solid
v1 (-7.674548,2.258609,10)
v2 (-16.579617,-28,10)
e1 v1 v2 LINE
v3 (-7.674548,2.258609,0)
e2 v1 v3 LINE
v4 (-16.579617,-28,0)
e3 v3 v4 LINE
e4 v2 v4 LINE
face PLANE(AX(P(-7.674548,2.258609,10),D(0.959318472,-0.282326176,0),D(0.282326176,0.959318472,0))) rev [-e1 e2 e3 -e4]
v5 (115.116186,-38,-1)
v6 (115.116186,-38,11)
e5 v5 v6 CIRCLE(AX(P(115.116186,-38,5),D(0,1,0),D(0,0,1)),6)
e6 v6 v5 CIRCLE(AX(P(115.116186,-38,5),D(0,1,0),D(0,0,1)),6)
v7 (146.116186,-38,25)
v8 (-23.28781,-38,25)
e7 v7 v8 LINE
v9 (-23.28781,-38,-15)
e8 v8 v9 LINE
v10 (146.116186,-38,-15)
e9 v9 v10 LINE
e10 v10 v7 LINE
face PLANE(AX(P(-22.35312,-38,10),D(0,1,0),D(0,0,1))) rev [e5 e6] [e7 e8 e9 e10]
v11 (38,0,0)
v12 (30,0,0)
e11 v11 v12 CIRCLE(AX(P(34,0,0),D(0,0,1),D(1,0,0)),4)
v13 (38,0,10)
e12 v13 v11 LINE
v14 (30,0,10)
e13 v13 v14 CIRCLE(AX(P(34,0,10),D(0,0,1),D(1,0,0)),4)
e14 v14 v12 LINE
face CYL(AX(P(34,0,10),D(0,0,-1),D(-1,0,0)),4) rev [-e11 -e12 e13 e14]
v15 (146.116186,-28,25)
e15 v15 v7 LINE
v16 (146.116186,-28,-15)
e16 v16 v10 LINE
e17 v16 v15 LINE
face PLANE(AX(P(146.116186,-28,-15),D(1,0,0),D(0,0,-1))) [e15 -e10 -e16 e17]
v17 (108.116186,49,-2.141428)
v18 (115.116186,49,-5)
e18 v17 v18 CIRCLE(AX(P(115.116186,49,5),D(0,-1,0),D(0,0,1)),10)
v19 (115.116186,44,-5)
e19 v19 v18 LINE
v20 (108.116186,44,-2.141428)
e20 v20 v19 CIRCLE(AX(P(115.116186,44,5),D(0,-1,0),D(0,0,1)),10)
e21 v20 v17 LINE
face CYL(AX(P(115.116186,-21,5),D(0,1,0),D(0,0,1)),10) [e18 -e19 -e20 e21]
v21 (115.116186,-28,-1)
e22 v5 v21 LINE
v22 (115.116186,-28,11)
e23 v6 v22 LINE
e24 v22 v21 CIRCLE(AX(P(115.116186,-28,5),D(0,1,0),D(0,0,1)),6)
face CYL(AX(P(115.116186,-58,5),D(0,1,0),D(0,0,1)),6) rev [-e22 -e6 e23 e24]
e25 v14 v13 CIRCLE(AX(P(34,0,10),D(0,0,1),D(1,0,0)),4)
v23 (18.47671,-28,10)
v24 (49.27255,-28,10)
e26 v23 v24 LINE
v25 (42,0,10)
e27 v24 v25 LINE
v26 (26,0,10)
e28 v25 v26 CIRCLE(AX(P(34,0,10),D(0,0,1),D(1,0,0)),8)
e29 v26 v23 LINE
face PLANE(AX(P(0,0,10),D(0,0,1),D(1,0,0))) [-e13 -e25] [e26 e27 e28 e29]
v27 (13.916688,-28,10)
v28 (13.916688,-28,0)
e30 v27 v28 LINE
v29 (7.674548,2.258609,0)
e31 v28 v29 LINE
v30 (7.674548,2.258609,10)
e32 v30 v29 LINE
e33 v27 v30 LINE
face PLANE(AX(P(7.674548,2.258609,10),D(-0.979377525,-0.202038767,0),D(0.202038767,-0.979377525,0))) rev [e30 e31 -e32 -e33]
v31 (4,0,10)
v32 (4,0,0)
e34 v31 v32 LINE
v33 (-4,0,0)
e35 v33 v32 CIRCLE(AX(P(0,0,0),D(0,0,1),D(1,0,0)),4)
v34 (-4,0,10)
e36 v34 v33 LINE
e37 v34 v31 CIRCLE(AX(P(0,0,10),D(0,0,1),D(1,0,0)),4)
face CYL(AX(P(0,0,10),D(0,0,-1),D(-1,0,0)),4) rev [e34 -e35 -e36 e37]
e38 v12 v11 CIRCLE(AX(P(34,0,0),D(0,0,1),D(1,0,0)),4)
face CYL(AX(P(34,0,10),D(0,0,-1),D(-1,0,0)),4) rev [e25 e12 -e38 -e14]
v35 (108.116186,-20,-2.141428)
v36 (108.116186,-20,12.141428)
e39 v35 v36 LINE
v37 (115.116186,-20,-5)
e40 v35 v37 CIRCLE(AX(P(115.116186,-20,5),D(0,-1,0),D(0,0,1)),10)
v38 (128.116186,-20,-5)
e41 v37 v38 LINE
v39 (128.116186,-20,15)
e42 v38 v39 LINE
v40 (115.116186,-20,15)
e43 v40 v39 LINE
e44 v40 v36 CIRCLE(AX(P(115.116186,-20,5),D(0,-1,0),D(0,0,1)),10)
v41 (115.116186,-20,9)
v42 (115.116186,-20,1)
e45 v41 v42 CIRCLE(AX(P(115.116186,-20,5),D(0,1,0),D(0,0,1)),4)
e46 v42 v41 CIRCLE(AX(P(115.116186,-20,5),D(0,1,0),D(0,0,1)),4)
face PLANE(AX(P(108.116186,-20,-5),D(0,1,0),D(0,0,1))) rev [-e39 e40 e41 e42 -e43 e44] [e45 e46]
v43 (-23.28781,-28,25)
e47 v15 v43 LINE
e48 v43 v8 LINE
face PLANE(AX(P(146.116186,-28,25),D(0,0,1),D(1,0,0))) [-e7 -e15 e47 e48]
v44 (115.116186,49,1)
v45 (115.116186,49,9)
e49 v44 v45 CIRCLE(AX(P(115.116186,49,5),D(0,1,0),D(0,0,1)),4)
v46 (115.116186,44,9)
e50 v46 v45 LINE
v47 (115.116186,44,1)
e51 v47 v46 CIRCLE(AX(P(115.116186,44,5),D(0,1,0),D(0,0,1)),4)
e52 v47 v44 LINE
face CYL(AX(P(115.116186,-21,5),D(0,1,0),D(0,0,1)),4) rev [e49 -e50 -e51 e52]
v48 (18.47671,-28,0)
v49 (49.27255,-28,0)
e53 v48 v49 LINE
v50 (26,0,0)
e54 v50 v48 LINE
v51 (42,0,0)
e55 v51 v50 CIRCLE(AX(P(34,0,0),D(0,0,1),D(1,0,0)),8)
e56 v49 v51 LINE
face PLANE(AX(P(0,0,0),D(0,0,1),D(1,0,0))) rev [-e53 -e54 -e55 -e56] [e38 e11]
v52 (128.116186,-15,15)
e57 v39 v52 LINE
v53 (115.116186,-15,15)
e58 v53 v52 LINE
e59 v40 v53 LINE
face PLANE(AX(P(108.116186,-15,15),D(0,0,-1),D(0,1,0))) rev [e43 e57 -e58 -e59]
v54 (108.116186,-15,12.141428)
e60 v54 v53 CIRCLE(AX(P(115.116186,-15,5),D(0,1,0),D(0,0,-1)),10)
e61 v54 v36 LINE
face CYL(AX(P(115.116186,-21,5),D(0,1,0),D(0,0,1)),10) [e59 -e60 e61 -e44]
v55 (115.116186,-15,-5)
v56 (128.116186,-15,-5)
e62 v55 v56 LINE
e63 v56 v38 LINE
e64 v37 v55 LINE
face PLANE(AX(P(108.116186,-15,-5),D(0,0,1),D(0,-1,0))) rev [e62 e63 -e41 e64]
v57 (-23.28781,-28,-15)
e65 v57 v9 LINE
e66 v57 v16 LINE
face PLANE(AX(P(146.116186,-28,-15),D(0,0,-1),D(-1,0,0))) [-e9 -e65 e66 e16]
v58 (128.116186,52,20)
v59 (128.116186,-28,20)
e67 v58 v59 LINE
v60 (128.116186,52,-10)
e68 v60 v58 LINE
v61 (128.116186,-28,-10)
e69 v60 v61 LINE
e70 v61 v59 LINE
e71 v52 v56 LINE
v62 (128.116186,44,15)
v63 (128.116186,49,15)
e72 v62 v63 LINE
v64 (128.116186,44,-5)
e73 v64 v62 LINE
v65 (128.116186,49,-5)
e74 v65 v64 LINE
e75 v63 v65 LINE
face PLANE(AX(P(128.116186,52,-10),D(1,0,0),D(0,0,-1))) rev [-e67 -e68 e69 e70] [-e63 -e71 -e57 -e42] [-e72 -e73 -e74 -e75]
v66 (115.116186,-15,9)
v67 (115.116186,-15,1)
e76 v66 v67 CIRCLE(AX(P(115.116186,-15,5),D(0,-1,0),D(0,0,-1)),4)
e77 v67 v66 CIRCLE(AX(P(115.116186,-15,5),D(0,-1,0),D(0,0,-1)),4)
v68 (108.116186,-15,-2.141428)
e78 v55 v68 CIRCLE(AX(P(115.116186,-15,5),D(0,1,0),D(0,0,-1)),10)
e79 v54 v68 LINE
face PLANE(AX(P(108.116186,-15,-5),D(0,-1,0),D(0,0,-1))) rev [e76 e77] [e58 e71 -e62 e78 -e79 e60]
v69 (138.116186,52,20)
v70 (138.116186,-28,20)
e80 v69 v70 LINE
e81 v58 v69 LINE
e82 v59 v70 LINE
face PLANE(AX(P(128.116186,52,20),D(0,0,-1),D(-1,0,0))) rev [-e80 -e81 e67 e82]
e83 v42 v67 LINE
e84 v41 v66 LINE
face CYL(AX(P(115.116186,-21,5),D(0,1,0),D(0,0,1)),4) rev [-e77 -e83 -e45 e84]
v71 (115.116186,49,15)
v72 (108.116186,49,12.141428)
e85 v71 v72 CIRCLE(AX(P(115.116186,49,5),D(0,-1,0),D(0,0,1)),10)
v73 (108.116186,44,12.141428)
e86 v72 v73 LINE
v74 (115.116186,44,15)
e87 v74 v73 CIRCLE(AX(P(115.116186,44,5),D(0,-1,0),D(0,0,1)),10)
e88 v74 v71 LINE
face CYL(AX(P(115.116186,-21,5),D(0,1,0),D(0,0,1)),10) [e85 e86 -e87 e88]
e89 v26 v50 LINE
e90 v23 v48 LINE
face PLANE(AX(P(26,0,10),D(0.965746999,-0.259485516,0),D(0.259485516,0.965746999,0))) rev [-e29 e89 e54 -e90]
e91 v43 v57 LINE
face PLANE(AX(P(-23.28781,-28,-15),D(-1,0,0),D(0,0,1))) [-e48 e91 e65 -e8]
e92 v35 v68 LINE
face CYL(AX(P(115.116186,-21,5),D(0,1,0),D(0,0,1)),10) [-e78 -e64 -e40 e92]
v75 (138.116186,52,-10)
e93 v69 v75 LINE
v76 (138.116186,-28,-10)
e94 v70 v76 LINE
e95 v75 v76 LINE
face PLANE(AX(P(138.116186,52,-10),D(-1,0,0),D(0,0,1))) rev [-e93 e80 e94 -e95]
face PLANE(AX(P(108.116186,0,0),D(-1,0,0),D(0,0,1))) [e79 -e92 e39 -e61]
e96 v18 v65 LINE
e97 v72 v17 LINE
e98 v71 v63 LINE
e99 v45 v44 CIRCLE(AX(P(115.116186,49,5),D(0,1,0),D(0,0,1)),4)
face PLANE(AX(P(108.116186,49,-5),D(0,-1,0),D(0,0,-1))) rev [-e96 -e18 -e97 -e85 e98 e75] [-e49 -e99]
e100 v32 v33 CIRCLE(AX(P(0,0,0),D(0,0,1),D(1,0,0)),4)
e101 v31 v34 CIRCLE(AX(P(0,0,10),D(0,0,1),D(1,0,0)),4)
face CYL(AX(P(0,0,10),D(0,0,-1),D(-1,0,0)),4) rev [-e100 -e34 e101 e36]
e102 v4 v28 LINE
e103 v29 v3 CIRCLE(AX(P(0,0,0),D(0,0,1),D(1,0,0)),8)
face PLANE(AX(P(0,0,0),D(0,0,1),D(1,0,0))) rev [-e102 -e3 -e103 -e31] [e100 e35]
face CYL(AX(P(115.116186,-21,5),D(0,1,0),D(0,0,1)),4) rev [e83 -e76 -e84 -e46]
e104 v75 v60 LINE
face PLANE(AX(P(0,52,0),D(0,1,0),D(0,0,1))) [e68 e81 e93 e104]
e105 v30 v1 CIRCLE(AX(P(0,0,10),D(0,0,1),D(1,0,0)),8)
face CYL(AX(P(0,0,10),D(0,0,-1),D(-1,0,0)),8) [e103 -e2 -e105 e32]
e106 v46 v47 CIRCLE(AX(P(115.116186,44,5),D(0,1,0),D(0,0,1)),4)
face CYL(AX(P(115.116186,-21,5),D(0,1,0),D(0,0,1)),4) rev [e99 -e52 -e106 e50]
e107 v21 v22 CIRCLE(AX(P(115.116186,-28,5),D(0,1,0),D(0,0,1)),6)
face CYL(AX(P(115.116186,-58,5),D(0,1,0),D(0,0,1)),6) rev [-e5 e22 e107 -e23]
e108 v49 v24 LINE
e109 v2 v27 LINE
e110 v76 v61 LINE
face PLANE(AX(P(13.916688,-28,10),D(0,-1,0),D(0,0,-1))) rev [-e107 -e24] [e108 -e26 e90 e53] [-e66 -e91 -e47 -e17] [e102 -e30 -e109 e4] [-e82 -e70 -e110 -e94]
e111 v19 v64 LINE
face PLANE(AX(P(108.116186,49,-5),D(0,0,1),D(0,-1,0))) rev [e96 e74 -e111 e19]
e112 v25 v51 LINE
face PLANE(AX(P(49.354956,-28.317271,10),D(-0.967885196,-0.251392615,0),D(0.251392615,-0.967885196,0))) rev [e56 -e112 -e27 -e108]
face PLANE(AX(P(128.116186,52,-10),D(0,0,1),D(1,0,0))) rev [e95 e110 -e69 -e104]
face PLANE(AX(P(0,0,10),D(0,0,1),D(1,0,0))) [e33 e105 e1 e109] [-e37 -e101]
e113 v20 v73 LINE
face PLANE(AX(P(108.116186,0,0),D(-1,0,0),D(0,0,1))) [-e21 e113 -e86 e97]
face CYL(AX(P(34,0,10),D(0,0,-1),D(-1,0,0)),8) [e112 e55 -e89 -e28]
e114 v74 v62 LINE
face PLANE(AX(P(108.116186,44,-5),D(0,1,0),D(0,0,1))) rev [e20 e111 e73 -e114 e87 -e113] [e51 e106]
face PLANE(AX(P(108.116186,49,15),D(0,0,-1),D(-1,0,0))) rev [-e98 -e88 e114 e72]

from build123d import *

# Parameters (mm, degrees)
SKETCH1_R           = 4
BOSS_EXTRUDE1_DEPTH = 10
SKETCH2_W           = 169.403995176
SKETCH2_H           = 40
BOSS_EXTRUDE2_DEPTH = 10
SKETCH3_W           = 10
SKETCH3_H           = 30
BOSS_EXTRUDE3_DEPTH = 80
SKETCH4_W           = 20
SKETCH4_H           = 5
BOSS_EXTRUDE4_DEPTH = 20
SKETCH5_R           = 4
CUT_EXTRUDE1_DEPTH  = 70
SKETCH6_R           = 6
CUT_EXTRUDE2_DEPTH  = 30


with BuildPart() as part:
    # Sketch1 → Boss-Extrude1 (new body)
    with BuildSketch(Plane.XY):
        with BuildLine():
            Line((-7.674547775, 2.258609406), (-16.579617078, -28))
            Line((-16.579617078, -28), (-22.35311977, -38))
            Line((-22.35311977, -38), (137.64688023, -38))
            Line((137.64688023, -38), (131.873377539, -28))
            Line((131.873377539, -28), (49.354955752, -28.3172709))
            Line((49.354955752, -28.3172709), (42, 0))
            ThreePointArc((42, 0), (34, 8), (26, 0))
            Line((26, 0), (18.4767103, -28))
            Line((18.4767103, -28), (13.916688293, -28))
            Line((13.916688293, -28), (7.674547775, 2.258609406))
            ThreePointArc((7.674547775, 2.258609406), (0, 8), (-7.674547775, 2.258609406))
        make_face()
        Circle(SKETCH1_R, mode=Mode.SUBTRACT)
        with Locations((34, 0)):
            Circle(SKETCH1_R, mode=Mode.SUBTRACT)
    extrude(amount=BOSS_EXTRUDE1_DEPTH)

    # Sketch2 → Boss-Extrude2 (add)
    with BuildSketch(Plane(origin=(0, -38, 0), x_dir=(-1, 0, 0), z_dir=(0, -1, 0))):
        with Locations((-61.414188083, -5)):
            Rectangle(SKETCH2_W, SKETCH2_H)
    extrude(amount=-BOSS_EXTRUDE2_DEPTH)

    # Sketch3 → Boss-Extrude3 (add)
    with BuildSketch(Plane(origin=(0, -28, 0), x_dir=(1, 0, 0), z_dir=(0, 1, 0))):
        with Locations((133.116185671, -5)):
            Rectangle(SKETCH3_W, SKETCH3_H)
    extrude(amount=BOSS_EXTRUDE3_DEPTH)

    # Sketch4 → Boss-Extrude4 (add)
    with BuildSketch(Plane.ZY.offset(-128.116185671)):
        with Locations((5, 46.5)):
            Rectangle(SKETCH4_W, SKETCH4_H)
        with Locations((5, -17.5)):
            Rectangle(SKETCH4_W, SKETCH4_H)
    extrude(amount=BOSS_EXTRUDE4_DEPTH)

    # Sketch5 → Cut-Extrude1 (cut)
    with BuildSketch(Plane(origin=(0, 49, 0), x_dir=(1, 0, 0), z_dir=(0, 1, 0))):
        with Locations(Location((115.116185671, -5, 0), (0, 0, 270))):
            Circle(SKETCH5_R)
        with BuildLine():
            Line((115.116185671, -15), (103.174329038, -18.113908317))
            Line((103.174329038, -18.113908317), (97.147243506, 5))
            Line((97.147243506, 5), (115.116185671, 5))
            ThreePointArc((115.116185671, 5), (105.116185671, -5), (115.116185671, -15))
        make_face()
    extrude(amount=-CUT_EXTRUDE1_DEPTH, mode=Mode.SUBTRACT)

    # Sketch6 → Cut-Extrude2 (cut)
    with BuildSketch(Plane(origin=(0, -28, 0), x_dir=(1, 0, 0), z_dir=(0, 1, 0))):
        with Locations(Location((115.116185671, -5, 0), (0, 0, 270))):
            Circle(SKETCH6_R)
    extrude(amount=-CUT_EXTRUDE2_DEPTH, mode=Mode.SUBTRACT)


solid = part.part
